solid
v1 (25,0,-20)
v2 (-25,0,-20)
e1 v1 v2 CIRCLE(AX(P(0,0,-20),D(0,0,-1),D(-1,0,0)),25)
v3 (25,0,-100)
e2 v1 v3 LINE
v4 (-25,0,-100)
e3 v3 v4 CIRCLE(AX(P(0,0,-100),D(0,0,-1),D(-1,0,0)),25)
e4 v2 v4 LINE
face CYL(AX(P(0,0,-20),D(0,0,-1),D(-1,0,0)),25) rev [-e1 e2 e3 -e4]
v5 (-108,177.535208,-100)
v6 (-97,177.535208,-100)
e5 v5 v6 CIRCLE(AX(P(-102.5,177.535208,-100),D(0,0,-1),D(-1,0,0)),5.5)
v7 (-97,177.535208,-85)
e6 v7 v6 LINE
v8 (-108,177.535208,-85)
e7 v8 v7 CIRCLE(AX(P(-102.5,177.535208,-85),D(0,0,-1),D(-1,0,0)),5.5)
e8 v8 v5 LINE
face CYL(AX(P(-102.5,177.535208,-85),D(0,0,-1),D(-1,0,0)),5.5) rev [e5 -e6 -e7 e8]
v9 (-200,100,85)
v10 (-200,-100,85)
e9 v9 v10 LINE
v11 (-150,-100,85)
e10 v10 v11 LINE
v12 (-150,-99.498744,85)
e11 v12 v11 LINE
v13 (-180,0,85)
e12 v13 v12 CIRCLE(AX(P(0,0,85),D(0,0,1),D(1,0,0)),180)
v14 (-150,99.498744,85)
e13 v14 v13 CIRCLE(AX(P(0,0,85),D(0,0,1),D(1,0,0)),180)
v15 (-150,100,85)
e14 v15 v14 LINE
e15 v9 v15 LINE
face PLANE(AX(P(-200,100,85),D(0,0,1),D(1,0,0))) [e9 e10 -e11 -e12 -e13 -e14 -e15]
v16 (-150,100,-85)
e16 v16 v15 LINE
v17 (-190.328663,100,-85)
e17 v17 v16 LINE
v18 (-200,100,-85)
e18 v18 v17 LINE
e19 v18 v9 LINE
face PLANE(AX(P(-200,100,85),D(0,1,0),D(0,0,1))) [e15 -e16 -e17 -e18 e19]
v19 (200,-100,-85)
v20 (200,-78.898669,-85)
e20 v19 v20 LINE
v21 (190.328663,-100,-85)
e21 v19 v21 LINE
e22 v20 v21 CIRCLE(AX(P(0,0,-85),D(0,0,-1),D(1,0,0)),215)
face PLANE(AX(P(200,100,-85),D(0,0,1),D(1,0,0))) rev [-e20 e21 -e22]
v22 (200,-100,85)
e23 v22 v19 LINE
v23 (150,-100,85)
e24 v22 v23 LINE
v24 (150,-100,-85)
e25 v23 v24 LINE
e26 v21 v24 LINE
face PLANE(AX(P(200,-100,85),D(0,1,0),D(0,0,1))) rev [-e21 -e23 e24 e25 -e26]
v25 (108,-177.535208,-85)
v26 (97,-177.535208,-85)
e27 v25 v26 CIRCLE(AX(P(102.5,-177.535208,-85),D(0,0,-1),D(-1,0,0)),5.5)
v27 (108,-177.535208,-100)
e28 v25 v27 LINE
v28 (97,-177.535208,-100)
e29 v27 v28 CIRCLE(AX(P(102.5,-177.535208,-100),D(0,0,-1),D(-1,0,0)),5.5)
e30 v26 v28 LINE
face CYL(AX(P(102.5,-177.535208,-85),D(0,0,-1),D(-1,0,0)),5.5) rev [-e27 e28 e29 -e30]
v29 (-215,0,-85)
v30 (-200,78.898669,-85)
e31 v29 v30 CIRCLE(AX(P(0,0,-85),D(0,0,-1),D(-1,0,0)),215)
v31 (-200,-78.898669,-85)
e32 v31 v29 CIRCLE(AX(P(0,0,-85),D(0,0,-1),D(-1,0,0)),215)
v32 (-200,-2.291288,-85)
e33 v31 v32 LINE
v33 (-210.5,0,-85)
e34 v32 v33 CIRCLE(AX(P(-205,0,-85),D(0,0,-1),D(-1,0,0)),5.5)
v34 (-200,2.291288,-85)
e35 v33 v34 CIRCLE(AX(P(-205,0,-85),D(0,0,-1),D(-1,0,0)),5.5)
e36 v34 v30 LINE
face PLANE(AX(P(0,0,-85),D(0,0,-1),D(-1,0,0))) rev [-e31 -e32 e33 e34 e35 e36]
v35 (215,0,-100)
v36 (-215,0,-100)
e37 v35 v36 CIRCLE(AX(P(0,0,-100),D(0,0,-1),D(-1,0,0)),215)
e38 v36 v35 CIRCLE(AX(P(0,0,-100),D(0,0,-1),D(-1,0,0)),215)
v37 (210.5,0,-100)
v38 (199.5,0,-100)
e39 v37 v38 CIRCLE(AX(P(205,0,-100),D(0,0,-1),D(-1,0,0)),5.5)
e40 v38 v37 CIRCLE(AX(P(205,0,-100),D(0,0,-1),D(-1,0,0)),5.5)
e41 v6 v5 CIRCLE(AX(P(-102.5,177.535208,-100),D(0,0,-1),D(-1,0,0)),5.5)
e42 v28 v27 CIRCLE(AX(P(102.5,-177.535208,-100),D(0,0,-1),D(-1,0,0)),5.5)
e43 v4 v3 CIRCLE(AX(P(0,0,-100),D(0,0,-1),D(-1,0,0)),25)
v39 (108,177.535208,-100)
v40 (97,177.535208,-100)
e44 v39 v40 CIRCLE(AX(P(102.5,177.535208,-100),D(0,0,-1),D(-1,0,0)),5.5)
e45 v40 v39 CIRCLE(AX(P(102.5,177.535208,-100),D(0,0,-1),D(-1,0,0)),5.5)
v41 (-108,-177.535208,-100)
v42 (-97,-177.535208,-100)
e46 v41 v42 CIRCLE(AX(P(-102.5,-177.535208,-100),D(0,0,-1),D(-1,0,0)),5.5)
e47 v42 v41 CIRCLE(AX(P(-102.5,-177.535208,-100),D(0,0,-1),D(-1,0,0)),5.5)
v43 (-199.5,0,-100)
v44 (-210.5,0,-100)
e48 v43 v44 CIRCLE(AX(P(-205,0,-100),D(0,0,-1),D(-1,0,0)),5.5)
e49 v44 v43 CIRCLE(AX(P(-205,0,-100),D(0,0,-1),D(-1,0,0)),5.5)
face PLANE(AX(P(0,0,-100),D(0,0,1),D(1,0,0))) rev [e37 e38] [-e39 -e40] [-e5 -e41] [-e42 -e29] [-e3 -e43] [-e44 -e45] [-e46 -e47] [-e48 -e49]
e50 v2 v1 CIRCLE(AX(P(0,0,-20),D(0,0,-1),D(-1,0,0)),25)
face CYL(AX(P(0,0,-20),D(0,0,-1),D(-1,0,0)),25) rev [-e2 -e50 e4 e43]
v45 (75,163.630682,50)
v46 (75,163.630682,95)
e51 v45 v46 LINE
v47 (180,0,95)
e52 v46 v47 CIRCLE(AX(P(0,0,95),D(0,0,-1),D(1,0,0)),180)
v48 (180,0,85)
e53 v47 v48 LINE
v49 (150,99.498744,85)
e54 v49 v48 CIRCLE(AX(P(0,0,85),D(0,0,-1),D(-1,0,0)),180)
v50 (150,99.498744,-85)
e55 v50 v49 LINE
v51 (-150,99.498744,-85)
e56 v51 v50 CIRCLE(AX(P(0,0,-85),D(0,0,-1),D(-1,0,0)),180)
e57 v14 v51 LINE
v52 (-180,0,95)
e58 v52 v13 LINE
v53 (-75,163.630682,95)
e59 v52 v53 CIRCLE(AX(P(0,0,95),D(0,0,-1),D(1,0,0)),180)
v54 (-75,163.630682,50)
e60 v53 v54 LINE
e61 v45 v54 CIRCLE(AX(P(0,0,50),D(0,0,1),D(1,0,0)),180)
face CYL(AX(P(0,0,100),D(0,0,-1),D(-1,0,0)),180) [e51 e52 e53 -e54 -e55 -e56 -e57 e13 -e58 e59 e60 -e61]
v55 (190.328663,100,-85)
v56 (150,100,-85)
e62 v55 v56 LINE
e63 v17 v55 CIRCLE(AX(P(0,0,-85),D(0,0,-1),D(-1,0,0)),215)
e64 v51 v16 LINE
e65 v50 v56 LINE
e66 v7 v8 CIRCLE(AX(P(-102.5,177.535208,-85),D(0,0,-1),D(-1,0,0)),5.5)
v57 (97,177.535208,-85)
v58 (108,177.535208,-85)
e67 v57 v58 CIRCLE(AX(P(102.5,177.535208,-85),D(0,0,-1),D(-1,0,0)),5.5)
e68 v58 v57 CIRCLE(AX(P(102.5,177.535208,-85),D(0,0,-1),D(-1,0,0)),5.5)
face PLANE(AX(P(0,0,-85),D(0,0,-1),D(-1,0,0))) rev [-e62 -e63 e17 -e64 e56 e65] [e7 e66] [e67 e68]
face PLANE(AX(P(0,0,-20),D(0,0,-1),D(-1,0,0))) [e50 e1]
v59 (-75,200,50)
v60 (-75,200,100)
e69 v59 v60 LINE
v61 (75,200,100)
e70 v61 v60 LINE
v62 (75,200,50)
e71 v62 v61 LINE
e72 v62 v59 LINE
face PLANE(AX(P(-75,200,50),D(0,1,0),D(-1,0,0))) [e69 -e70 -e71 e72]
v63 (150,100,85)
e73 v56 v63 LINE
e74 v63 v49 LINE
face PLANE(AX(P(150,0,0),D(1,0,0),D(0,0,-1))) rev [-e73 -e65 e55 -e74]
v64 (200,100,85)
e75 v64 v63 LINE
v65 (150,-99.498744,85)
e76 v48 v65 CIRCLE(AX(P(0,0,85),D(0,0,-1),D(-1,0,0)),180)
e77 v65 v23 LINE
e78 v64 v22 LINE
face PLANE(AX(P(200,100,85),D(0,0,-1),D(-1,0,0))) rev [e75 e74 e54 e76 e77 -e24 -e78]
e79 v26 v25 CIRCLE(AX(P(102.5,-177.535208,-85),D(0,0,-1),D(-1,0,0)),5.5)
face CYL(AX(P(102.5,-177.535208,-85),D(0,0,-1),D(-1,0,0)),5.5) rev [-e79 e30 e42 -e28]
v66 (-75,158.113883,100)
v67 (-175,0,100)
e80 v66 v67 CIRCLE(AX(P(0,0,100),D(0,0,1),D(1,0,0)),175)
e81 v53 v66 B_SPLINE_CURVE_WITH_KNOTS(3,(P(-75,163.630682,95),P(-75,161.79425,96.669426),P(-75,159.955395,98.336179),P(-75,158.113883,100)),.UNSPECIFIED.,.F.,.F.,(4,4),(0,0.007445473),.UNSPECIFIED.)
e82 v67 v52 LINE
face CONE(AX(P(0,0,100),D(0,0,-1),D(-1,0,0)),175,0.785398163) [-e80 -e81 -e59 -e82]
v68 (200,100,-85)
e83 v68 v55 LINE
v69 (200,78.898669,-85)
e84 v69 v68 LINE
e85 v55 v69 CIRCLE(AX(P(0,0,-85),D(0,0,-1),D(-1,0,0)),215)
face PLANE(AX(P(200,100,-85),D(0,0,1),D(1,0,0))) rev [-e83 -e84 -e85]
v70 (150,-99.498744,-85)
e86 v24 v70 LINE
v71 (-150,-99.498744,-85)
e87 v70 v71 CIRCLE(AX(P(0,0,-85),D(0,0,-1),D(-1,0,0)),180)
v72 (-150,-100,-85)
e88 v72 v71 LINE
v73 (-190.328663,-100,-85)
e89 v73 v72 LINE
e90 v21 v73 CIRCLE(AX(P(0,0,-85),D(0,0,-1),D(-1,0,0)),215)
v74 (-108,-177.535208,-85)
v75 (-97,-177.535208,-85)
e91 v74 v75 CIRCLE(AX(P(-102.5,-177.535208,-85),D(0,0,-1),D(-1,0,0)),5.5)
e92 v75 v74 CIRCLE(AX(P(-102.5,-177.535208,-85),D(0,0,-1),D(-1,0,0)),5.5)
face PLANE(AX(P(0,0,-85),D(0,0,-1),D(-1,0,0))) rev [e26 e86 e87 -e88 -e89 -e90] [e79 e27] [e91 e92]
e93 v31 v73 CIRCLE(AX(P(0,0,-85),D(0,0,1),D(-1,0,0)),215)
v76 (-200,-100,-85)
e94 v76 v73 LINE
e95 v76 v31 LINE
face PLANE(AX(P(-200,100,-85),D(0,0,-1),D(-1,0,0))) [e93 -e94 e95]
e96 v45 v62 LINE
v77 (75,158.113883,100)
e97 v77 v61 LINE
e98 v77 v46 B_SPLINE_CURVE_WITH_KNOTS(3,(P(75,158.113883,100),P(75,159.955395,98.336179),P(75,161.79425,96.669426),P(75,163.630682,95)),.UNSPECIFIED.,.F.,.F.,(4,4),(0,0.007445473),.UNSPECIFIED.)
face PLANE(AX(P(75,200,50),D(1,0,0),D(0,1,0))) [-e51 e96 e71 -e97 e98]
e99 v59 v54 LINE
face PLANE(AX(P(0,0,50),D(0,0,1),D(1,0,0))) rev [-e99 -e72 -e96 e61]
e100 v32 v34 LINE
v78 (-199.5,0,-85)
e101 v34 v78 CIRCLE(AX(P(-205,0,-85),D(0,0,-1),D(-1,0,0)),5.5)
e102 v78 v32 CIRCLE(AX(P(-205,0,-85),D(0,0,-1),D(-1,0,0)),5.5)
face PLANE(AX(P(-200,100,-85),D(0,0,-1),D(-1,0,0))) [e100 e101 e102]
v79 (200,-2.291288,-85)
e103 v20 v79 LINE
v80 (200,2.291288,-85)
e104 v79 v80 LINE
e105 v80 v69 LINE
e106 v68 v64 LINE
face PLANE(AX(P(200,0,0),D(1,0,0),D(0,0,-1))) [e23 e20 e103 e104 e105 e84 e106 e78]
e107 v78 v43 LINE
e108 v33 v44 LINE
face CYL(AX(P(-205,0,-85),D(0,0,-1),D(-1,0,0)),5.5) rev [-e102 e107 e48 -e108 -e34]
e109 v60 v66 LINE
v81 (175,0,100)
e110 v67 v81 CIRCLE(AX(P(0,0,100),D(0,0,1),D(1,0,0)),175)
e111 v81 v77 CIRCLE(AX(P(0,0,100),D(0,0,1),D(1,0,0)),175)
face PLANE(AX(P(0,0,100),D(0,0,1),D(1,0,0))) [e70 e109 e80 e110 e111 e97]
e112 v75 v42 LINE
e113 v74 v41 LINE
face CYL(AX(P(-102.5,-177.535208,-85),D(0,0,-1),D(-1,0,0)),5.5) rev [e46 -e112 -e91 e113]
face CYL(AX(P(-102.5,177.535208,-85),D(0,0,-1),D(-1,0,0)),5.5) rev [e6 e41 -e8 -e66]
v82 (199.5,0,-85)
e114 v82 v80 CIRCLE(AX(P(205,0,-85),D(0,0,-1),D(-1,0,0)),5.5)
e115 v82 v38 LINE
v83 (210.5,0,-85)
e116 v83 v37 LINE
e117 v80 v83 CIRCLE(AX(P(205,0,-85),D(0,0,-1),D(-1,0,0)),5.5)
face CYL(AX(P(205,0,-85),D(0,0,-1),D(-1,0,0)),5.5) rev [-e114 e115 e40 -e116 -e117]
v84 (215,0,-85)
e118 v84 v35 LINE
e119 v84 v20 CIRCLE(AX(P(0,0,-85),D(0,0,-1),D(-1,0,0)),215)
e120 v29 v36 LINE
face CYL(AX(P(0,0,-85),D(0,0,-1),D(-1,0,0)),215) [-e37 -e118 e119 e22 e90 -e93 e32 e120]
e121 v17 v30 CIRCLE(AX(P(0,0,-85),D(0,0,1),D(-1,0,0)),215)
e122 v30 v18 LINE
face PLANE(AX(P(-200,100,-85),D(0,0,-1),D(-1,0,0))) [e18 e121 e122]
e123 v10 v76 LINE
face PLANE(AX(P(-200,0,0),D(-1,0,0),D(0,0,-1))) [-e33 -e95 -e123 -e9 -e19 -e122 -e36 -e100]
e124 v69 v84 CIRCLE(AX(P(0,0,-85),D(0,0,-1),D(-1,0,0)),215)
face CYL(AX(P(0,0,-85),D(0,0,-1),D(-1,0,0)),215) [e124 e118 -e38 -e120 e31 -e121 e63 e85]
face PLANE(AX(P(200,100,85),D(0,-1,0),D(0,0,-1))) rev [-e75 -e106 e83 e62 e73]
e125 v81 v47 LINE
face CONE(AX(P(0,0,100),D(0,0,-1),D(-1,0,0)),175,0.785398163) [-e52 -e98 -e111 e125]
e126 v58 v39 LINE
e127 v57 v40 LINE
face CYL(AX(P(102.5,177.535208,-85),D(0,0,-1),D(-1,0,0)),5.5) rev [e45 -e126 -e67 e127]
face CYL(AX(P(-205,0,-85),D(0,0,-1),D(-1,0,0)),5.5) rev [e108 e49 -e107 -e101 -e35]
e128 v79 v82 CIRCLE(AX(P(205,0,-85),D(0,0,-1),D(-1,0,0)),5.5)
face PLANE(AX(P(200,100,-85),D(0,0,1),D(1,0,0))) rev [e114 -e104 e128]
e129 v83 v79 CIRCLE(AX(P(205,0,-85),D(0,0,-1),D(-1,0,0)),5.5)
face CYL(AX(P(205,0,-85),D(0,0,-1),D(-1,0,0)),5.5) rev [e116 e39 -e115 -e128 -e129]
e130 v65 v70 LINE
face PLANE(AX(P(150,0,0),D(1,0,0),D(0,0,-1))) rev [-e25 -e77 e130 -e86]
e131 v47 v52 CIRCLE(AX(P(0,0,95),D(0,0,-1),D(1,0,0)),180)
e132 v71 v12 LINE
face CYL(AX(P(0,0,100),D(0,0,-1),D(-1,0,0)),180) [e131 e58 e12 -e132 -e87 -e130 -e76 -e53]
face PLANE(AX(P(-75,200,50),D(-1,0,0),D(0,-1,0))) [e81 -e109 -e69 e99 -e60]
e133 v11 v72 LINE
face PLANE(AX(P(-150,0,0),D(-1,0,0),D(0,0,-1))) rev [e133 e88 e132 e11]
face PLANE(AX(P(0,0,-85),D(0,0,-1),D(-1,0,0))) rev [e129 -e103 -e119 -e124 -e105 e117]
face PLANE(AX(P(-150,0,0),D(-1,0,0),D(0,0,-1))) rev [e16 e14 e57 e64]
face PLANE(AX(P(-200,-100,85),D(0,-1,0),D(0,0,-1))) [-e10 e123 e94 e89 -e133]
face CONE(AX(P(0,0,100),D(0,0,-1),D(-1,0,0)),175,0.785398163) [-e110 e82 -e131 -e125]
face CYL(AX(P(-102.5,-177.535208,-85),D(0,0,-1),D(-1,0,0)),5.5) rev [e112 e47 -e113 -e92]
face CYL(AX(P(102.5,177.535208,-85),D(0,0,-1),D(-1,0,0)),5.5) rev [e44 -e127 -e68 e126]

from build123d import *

# Parameters (mm, degrees)
SKETCH1_R           = 180
BOSS_EXTRUDE1_DEPTH = 100
SKETCH2_R           = 25
CUT_EXTRUDE1_DEPTH  = 80
SKETCH3_W           = 150
SKETCH3_H           = 62.418974348
BOSS_EXTRUDE3_DEPTH = 50
BOSS_EXTRUDE4_START = -15
SKETCH4_R           = 215
SKETCH4_R_2         = 180
SKETCH4_R_3         = 5.5
BOSS_EXTRUDE4_DEPTH = 15
CHAMFER1_SIZE       = 5
BOSS_EXTRUDE5_START = 150
SKETCH5_W           = 170
SKETCH5_H           = 200
BOSS_EXTRUDE5_DEPTH = 50


with BuildPart() as part:
    # Sketch1 → Boss-Extrude1 (new, symmetric)
    with BuildSketch(Plane.XY):
        Circle(SKETCH1_R)
    extrude(amount=BOSS_EXTRUDE1_DEPTH, both=True)

    # Sketch2 → Cut-Extrude1 (cut)
    with BuildSketch(Plane(origin=(0, 0, -100), x_dir=(-1, 0, 0), z_dir=(0, 0, -1))):
        Circle(SKETCH2_R)
    extrude(amount=-CUT_EXTRUDE1_DEPTH, mode=Mode.SUBTRACT)

    # Sketch3 → Boss-Extrude3 (add)
    with BuildSketch(Plane.XY.offset(100)):
        with Locations((0, 168.790512826)):
            Rectangle(SKETCH3_W, SKETCH3_H)
    extrude(amount=-BOSS_EXTRUDE3_DEPTH)

    # Sketch4 → Boss-Extrude4 (add)
    with BuildSketch(Plane(origin=(0, 0, -100), x_dir=(-1, 0, 0), z_dir=(0, 0, -1)).offset(BOSS_EXTRUDE4_START)):
        Circle(SKETCH4_R)
        Circle(SKETCH4_R_2, mode=Mode.SUBTRACT)
        with Locations((-102.5, 177.535207776)):
            Circle(SKETCH4_R_3, mode=Mode.SUBTRACT)
        with Locations((102.5, 177.535207776)):
            Circle(SKETCH4_R_3, mode=Mode.SUBTRACT)
        with Locations((205, 0)):
            Circle(SKETCH4_R_3, mode=Mode.SUBTRACT)
        with Locations((102.5, -177.535207776)):
            Circle(SKETCH4_R_3, mode=Mode.SUBTRACT)
        with Locations((-102.5, -177.535207776)):
            Circle(SKETCH4_R_3, mode=Mode.SUBTRACT)
        with Locations((-205, 0)):
            Circle(SKETCH4_R_3, mode=Mode.SUBTRACT)
    extrude(amount=BOSS_EXTRUDE4_DEPTH)

    # Chamfer1
    chamfer1_edges = [part.edges().sort_by_distance(p)[0] for p in [
        (-97.211110476, -151.492574075, 100),
    ]]
    chamfer(chamfer1_edges, length=CHAMFER1_SIZE)

    # Sketch5 → Boss-Extrude5 (add)
    with BuildSketch(Plane(origin=(0, 0, 0), x_dir=(0, 0, -1), z_dir=(1, 0, 0)).offset(BOSS_EXTRUDE5_START)):
        Rectangle(SKETCH5_W, SKETCH5_H)
    boss_extrude5 = extrude(amount=BOSS_EXTRUDE5_DEPTH)

    # Mirror1: Boss-Extrude5 across plane
    add(boss_extrude5.mirror(Plane(origin=(0, 0, 0), x_dir=(0, 0, 1), z_dir=(1, 0, 0))))


solid = part.part
